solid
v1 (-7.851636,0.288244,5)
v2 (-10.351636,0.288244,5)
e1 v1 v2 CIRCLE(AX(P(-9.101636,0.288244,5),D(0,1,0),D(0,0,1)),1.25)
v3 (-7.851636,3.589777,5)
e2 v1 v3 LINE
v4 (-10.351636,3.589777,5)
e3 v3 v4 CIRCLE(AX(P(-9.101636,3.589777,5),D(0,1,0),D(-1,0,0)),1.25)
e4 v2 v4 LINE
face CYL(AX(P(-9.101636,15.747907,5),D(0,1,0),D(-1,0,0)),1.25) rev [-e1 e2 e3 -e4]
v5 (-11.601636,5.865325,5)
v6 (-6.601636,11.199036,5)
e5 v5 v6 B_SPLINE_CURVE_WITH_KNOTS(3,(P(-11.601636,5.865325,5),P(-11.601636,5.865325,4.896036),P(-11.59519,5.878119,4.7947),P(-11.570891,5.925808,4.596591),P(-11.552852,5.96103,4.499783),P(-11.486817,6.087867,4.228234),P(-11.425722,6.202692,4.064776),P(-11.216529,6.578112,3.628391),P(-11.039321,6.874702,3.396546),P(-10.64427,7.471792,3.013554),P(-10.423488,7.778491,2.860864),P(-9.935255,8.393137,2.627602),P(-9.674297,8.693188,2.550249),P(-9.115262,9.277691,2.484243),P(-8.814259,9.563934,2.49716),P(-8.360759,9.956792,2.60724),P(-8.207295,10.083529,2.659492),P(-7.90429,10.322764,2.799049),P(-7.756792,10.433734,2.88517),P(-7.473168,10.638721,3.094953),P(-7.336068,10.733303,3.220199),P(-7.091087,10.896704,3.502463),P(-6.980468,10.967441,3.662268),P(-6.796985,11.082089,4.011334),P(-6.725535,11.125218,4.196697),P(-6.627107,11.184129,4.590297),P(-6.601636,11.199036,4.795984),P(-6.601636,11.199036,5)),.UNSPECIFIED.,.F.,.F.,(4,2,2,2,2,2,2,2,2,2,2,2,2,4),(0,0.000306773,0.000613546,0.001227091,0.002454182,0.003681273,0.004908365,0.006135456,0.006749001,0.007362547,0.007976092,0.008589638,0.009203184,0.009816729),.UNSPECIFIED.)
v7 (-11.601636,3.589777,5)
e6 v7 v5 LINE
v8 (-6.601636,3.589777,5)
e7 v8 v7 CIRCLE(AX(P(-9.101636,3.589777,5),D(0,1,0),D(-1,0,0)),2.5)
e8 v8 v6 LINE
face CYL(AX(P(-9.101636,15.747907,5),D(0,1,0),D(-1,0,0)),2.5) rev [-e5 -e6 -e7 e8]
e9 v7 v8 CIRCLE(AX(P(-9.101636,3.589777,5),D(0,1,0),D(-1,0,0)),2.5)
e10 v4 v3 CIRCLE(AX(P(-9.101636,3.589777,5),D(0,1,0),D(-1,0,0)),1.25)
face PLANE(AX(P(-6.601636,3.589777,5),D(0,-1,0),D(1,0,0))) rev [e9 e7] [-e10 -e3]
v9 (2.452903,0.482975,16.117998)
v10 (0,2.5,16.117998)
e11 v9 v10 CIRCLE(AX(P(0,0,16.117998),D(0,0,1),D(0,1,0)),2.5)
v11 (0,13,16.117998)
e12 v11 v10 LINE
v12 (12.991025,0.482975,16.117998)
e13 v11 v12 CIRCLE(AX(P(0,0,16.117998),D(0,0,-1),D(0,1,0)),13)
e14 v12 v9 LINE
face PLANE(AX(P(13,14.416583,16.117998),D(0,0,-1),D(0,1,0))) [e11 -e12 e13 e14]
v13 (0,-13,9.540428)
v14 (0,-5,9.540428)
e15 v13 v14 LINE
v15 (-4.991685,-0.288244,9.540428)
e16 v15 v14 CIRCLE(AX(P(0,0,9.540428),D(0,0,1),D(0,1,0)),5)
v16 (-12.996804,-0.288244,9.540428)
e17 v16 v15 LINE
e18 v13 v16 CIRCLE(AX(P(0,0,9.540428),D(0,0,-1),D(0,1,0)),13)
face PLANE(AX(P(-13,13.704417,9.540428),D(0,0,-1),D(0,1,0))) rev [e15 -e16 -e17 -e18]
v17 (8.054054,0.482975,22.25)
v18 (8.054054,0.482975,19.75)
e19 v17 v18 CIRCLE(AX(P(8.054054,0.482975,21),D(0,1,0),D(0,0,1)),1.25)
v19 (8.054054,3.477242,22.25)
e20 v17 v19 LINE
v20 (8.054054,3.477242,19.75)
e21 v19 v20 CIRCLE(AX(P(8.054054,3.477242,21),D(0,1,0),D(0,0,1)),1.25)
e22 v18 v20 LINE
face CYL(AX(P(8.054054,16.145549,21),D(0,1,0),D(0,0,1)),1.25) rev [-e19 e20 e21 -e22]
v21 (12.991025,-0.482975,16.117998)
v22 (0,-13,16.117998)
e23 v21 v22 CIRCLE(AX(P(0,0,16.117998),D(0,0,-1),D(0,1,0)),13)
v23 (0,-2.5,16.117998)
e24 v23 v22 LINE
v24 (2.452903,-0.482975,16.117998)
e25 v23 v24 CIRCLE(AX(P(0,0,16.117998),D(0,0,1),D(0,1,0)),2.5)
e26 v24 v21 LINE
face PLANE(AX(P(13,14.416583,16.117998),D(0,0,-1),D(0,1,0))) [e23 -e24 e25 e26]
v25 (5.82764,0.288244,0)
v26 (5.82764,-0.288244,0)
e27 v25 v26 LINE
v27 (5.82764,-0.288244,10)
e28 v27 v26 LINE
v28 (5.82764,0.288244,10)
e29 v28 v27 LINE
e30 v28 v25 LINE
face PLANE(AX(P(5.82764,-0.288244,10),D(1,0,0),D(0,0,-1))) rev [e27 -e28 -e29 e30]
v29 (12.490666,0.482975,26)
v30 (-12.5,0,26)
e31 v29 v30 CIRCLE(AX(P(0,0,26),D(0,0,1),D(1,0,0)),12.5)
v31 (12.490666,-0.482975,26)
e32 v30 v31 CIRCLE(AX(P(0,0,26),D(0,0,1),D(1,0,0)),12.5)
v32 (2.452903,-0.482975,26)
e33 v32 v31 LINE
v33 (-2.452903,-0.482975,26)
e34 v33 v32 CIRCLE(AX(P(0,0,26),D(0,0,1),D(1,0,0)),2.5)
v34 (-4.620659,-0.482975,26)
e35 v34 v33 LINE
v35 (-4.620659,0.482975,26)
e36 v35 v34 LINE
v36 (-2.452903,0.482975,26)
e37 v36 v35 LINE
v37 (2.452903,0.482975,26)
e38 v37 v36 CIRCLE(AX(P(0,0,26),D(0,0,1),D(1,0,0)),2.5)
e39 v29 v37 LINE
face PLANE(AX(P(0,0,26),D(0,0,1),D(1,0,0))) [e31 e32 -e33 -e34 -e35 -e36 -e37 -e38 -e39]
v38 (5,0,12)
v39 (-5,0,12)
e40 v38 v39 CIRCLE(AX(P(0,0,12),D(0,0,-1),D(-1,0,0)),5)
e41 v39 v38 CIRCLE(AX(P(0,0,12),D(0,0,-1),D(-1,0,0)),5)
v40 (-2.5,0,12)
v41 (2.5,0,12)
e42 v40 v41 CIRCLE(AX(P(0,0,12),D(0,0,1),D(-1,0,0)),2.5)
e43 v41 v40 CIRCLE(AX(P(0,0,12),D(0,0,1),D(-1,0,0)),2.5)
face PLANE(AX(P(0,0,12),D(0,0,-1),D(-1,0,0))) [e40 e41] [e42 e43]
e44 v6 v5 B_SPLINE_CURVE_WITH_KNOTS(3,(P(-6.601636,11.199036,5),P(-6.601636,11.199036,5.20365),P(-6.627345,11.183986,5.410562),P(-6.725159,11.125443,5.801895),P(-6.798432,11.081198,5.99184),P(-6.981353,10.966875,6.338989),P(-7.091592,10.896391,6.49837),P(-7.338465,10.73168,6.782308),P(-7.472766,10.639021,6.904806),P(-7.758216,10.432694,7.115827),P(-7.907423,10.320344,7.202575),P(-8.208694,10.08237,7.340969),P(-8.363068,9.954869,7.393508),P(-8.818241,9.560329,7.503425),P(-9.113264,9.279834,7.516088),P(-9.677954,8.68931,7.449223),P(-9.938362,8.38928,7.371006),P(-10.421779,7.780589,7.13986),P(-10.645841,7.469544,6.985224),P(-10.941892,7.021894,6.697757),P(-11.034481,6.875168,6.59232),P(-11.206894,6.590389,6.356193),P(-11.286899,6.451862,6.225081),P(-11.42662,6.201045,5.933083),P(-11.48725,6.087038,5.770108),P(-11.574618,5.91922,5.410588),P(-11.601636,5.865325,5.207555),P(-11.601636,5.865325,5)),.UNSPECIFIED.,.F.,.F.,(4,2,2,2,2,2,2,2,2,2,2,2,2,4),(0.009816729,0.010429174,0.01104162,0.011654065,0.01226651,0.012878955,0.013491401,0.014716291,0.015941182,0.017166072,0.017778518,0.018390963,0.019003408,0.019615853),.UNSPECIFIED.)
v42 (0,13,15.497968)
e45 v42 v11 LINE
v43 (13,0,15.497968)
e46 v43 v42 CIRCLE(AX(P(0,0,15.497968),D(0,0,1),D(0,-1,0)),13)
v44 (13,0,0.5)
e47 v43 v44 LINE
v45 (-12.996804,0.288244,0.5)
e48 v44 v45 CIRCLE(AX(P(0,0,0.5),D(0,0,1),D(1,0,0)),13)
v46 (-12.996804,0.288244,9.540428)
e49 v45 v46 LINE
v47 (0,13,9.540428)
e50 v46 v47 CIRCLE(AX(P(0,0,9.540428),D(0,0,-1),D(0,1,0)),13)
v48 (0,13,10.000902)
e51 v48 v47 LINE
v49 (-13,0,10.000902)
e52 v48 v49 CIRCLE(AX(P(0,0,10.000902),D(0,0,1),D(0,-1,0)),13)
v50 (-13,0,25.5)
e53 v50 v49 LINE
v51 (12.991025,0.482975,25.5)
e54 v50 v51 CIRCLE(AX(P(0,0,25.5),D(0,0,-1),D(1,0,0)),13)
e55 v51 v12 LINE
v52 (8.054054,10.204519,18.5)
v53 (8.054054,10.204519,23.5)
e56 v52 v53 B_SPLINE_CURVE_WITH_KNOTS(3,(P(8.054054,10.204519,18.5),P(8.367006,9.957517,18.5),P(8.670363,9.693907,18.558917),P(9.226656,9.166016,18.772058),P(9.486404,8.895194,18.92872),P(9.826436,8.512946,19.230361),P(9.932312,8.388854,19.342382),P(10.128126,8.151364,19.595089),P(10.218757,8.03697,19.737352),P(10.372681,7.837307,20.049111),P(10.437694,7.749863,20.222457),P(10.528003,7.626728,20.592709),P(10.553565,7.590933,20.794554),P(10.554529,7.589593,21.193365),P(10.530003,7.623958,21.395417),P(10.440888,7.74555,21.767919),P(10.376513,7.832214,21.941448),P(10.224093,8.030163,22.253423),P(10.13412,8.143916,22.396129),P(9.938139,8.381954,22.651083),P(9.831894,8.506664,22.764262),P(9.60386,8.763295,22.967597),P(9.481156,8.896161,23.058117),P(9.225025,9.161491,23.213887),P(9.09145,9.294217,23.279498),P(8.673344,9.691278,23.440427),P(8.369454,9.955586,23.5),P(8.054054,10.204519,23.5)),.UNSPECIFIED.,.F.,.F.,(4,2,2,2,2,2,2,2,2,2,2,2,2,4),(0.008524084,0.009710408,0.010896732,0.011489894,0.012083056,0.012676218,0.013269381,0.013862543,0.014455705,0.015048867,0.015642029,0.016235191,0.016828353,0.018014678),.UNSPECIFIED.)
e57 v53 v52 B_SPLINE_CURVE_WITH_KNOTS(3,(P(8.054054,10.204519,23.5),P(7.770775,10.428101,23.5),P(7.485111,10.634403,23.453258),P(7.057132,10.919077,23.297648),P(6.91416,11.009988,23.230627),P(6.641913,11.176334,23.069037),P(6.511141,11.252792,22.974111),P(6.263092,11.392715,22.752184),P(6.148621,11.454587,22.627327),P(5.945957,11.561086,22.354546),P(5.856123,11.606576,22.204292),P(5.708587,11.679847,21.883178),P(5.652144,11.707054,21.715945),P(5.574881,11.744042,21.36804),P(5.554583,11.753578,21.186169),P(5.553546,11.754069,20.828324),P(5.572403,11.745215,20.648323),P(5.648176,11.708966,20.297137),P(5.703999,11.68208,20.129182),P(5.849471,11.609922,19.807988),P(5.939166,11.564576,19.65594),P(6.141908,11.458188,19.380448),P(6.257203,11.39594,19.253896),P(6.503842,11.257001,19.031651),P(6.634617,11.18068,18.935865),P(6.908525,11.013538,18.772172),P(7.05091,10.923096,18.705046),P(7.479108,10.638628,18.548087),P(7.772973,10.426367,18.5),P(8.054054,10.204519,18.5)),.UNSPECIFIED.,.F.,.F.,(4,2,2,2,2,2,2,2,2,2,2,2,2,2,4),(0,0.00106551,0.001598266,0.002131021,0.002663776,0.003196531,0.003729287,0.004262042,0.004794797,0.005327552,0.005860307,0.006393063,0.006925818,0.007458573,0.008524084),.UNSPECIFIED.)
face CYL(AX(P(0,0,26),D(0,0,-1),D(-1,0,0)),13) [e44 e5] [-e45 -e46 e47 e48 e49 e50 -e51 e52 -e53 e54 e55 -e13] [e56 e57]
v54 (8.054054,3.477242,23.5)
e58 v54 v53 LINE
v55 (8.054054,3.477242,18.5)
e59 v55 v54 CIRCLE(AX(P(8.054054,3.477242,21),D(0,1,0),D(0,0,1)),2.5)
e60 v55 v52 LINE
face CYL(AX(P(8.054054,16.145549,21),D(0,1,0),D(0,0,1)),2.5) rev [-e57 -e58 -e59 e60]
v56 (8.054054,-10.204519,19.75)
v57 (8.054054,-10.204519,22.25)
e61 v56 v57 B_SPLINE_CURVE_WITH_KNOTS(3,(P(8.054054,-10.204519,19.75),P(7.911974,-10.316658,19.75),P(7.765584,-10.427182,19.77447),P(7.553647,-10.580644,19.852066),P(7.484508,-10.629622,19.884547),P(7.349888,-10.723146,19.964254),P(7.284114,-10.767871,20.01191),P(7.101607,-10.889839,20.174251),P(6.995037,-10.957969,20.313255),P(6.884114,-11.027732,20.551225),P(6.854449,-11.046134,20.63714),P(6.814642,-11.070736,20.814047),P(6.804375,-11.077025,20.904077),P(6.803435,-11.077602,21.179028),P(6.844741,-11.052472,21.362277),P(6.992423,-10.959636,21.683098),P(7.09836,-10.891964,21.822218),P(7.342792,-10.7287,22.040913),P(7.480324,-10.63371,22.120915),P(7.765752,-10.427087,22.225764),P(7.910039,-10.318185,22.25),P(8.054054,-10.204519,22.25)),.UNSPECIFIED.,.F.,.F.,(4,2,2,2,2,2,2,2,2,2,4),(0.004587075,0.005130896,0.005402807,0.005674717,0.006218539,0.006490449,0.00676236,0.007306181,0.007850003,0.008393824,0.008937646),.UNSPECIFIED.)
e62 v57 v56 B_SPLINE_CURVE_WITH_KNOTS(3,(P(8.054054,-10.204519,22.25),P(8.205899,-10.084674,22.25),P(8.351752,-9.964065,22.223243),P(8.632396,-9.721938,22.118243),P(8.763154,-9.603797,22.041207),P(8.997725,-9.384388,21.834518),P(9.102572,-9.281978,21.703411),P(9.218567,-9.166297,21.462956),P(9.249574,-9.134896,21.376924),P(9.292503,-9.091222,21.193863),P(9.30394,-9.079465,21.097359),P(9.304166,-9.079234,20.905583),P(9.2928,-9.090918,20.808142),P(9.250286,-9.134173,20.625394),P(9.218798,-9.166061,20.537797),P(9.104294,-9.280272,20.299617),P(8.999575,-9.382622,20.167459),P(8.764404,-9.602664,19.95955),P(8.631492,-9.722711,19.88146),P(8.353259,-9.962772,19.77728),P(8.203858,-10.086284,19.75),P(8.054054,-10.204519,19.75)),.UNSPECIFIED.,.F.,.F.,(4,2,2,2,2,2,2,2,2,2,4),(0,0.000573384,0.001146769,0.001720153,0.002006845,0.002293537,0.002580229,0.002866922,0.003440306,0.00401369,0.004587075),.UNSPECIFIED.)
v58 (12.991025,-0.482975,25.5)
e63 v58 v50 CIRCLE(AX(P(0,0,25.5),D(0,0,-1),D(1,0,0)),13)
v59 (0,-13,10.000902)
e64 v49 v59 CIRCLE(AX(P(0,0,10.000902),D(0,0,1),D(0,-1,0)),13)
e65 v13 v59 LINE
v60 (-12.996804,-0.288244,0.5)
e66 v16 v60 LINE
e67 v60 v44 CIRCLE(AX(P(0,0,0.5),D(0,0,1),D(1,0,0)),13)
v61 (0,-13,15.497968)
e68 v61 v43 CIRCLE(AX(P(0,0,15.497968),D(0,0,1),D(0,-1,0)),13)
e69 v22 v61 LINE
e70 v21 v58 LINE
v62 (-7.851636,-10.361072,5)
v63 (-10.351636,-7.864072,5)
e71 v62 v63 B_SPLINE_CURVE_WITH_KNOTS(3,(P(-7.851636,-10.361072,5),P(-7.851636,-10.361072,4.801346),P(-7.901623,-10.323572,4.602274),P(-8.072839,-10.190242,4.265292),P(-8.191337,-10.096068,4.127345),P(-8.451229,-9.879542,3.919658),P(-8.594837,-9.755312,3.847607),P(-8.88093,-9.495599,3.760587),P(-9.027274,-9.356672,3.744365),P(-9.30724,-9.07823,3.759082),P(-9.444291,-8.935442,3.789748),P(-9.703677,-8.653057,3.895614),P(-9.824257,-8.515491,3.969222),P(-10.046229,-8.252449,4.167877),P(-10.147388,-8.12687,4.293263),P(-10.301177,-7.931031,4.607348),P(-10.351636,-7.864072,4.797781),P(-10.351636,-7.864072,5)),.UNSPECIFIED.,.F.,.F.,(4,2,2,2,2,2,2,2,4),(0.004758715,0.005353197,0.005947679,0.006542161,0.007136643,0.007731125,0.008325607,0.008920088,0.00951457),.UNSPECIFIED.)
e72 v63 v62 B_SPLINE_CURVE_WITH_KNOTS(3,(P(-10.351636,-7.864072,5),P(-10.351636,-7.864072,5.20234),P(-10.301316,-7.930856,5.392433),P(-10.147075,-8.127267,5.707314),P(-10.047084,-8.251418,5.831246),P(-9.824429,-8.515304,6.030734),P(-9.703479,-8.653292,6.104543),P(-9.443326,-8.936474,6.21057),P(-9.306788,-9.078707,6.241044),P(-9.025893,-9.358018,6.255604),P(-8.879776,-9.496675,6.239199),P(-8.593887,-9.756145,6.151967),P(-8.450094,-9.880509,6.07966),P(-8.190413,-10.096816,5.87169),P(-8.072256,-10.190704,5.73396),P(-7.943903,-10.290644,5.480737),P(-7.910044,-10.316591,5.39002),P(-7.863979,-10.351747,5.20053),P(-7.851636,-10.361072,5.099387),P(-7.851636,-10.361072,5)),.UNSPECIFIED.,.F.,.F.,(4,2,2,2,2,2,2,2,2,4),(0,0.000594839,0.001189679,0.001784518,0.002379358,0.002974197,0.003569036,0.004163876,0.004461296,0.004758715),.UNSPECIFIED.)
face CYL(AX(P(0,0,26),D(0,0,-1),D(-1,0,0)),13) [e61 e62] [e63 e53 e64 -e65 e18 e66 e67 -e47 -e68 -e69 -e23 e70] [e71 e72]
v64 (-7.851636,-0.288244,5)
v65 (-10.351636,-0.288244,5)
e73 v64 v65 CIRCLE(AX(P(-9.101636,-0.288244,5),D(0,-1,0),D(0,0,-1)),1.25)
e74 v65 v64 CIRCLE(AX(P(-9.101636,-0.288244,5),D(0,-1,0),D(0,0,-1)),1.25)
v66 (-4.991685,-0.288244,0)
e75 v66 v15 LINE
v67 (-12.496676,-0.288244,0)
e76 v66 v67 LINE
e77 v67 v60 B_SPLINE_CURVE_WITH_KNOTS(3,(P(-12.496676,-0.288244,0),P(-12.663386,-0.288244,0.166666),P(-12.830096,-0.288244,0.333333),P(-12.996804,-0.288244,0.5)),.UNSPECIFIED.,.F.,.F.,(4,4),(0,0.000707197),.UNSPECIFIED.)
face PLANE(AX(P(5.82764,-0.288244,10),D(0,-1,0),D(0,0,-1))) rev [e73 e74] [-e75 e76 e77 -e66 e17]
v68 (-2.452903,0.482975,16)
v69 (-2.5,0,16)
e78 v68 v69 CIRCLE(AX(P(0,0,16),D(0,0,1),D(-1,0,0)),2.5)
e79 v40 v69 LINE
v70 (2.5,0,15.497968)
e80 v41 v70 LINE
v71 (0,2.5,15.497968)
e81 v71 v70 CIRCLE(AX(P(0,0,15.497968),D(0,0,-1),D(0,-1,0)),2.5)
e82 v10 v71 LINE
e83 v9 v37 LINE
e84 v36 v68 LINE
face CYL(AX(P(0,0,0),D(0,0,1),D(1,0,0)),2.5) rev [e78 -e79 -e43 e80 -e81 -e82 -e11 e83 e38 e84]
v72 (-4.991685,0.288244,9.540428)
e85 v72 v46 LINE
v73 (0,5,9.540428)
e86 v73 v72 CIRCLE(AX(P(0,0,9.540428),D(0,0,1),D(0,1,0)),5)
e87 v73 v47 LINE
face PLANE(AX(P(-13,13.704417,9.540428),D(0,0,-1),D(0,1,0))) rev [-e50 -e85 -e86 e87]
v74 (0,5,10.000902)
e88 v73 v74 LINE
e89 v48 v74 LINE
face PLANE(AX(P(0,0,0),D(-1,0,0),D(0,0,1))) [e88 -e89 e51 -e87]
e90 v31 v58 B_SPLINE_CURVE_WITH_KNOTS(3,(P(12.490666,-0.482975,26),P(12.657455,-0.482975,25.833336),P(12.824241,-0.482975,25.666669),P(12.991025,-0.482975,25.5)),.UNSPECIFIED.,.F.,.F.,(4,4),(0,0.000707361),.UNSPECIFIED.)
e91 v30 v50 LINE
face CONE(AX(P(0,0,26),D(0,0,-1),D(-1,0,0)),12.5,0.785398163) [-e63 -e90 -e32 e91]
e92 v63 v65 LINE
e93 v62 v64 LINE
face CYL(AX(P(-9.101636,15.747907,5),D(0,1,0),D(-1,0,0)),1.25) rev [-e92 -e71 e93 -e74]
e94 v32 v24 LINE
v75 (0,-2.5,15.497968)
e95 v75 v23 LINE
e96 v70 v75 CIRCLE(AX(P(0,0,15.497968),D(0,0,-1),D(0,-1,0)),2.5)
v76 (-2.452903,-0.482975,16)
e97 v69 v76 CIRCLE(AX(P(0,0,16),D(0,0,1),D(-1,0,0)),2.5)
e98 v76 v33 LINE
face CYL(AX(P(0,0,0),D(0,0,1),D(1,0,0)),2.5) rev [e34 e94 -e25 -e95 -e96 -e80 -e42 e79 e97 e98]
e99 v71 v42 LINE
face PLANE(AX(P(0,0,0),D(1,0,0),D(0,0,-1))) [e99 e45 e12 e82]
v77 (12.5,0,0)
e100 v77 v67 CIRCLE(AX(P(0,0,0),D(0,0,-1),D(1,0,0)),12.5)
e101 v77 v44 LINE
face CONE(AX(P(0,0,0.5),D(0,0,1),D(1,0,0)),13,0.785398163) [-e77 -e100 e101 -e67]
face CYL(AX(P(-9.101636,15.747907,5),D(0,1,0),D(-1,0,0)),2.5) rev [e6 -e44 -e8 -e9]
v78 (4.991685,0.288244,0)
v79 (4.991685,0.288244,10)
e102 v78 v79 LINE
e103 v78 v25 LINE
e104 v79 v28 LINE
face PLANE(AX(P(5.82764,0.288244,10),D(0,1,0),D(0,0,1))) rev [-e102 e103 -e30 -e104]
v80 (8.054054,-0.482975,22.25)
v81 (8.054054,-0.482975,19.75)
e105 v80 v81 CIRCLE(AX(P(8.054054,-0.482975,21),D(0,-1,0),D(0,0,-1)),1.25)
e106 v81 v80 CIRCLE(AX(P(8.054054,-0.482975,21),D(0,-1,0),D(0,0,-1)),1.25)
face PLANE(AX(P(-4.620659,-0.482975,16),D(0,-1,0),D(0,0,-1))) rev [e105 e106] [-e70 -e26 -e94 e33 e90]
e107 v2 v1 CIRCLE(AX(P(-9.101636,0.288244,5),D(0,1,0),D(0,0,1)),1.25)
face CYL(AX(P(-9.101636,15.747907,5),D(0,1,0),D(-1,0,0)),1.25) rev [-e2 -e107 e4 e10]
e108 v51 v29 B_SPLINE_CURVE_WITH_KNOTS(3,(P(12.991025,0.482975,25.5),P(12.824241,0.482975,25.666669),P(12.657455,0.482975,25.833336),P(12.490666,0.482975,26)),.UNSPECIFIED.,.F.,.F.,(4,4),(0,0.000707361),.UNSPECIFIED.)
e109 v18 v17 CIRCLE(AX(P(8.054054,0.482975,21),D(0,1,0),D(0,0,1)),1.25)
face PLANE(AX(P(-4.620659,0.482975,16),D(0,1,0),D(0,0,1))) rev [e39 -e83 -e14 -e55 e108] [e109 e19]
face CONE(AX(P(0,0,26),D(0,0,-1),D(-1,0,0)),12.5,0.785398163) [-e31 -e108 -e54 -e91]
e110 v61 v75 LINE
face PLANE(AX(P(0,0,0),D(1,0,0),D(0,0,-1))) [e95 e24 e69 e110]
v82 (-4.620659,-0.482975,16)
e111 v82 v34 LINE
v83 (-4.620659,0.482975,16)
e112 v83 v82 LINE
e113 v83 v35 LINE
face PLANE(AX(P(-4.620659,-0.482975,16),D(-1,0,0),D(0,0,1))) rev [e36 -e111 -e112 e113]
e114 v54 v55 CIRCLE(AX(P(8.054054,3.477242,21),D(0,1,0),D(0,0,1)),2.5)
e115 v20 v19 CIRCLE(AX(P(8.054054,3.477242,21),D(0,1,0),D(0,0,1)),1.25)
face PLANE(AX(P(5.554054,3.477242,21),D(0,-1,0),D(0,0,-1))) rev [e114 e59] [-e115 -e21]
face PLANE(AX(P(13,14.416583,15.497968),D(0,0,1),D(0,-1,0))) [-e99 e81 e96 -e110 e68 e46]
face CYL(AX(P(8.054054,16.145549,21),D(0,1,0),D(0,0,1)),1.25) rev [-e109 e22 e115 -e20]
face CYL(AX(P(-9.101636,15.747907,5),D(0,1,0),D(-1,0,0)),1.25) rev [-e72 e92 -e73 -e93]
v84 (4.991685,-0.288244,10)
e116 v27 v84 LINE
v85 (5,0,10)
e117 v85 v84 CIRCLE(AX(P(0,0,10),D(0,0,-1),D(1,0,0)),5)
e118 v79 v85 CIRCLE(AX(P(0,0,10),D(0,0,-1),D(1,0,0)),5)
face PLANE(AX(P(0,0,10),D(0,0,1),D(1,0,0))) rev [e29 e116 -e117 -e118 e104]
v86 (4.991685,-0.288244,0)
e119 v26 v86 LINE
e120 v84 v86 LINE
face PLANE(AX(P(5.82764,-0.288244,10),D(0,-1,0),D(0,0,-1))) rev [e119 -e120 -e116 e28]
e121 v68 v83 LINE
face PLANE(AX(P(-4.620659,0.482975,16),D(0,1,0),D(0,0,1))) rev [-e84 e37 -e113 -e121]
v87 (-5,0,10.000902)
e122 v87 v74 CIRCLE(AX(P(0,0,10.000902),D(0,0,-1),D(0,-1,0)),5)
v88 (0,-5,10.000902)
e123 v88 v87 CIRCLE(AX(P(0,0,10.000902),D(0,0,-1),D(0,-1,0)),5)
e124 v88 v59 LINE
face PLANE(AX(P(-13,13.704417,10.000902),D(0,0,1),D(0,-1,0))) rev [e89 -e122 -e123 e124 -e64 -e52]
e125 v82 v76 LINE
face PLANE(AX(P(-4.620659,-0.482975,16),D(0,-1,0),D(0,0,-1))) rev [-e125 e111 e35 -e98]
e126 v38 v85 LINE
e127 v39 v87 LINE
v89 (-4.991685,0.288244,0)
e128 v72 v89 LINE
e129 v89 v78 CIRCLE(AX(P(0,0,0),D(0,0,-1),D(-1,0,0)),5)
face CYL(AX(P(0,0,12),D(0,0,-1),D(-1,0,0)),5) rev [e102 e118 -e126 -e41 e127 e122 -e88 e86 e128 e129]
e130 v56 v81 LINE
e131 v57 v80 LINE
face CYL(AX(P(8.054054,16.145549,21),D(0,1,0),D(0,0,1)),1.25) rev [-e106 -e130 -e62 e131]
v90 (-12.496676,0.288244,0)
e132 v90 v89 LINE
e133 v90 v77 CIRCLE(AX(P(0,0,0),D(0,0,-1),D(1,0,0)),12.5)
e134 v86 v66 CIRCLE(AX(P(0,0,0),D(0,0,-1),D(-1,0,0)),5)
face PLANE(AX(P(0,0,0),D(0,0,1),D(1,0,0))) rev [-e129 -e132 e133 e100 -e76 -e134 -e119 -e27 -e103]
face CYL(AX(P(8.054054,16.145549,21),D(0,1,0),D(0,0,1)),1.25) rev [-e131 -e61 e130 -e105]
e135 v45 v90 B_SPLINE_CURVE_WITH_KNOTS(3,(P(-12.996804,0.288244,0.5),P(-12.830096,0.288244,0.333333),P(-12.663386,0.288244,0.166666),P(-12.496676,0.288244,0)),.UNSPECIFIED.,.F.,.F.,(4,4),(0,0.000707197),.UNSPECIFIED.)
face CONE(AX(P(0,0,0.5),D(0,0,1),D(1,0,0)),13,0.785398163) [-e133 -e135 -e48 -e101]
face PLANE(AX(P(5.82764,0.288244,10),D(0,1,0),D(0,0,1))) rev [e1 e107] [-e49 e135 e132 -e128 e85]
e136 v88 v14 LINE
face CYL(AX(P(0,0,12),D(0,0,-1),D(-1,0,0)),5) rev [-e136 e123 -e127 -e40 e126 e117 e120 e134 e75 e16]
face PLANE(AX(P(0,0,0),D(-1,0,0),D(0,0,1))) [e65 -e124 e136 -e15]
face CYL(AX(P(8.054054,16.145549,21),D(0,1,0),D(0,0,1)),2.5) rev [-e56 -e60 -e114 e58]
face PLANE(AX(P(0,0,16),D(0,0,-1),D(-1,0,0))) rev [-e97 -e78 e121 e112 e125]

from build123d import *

# Parameters (mm, degrees)
SKETCH_1_R          = 13
EXTRUDE_1_DEPTH     = 26
SKETCH_2_R          = 2.5
CUT_EXTRUDE_1_DEPTH = 32.843366656
SKETCH_3_R          = 5
CUT_EXTRUDE_2_DEPTH = 12
SKETCH_4_W          = 21.947389444
SKETCH_4_H          = 0.965950114
CUT_EXTRUDE_3_DEPTH = 10
SKETCH_5_W          = 24.42165542
SKETCH_5_H          = 0.576488958
CUT_EXTRUDE_4_DEPTH = 10
SKETCH_6_W          = 0.620030038
SKETCH_6_H          = 28.40124723
CUT_EXTRUDE_5_DEPTH = 32.843366656
SKETCH_7_W          = 0.460474017
SKETCH_7_H          = 28.978503402
CUT_EXTRUDE_6_DEPTH = 32.843366656
CHAMFER_1_SIZE      = 0.5


with BuildPart() as part:
    # 草图1 → 凸台-拉伸1 (new body)
    with BuildSketch(Plane.XY):
        with Locations(Location((0, 0, 0), (0, 0, 180))):
            Circle(SKETCH_1_R)
    extrude(amount=EXTRUDE_1_DEPTH)

    # 草图2 → 切除-拉伸1 (cut, through all)
    with BuildSketch(Plane.XY.offset(26)):
        Circle(SKETCH_2_R)
    extrude(amount=-CUT_EXTRUDE_1_DEPTH, mode=Mode.SUBTRACT)

    # 草图3 → 切除-拉伸2 (cut)
    with BuildSketch(Plane(origin=(0, 0, 0), x_dir=(-1, 0, 0), z_dir=(0, 0, -1))):
        Circle(SKETCH_3_R)
    extrude(amount=-CUT_EXTRUDE_2_DEPTH, mode=Mode.SUBTRACT)

    # 草图4 → 切除-拉伸3 (cut)
    with BuildSketch(Plane.XY.offset(26)):
        with Locations((6.353035437, 0)):
            Rectangle(SKETCH_4_W, SKETCH_4_H)
    extrude(amount=-CUT_EXTRUDE_3_DEPTH, mode=Mode.SUBTRACT)

    # 草图5 → 切除-拉伸4 (cut)
    with BuildSketch(Plane(origin=(0, 0, 0), x_dir=(-1, 0, 0), z_dir=(0, 0, -1))):
        with Locations((6.383187544, 0)):
            Rectangle(SKETCH_5_W, SKETCH_5_H)
    extrude(amount=-CUT_EXTRUDE_4_DEPTH, mode=Mode.SUBTRACT)

    # 草图6 → 切除-拉伸5 (cut, through all)
    with BuildSketch(Plane(origin=(0, 0, 0), x_dir=(0, 0, -1), z_dir=(1, 0, 0))):
        with Locations((-15.807983144, 0.215959177)):
            Rectangle(SKETCH_6_W, SKETCH_6_H)
    extrude(amount=CUT_EXTRUDE_5_DEPTH, mode=Mode.SUBTRACT)

    # 草图7 → 切除-拉伸6 (cut, through all)
    with BuildSketch(Plane(origin=(0, 0, 0), x_dir=(0, 0, -1), z_dir=(1, 0, 0))):
        with Locations((-9.770664876, -0.784834467)):
            Rectangle(SKETCH_7_W, SKETCH_7_H)
    extrude(amount=-CUT_EXTRUDE_6_DEPTH, mode=Mode.SUBTRACT)

    # 草图8 → 切除-旋转1 (revolve, cut)
    with BuildSketch(Plane.XY.offset(21), mode=Mode.PRIVATE) as cut_revolve_1_sk:
        Polygon((5.554054174, 13), (5.554054174, 3.477242408), (6.804054174, 3.477242408), (6.804054174, -12.992472662), (8.054054174, -12.992472662), (8.054054174, 13), align=None)
    revolve(cut_revolve_1_sk.sketch.rotate(Axis((8.054054174, 16.145548825, 21), (0, -1, 0)), 270), axis=Axis((8.054054174, 16.145548825, 21), (0, -1, 0)), mode=Mode.SUBTRACT)

    # 草图9 → 切除-旋转2 (revolve, cut)
    with BuildSketch(Plane(origin=(0, 0, 5), x_dir=(-1, 0, 0), z_dir=(0, 0, -1)), mode=Mode.PRIVATE) as cut_revolve_2_sk:
        Polygon((6.601636039, 12.445267502), (6.601636039, 3.589776819), (7.851636039, 3.589776819), (7.851636039, -11.887089541), (9.101636039, -11.887089541), (9.101636039, 12.445267502), align=None)
    revolve(cut_revolve_2_sk.sketch.rotate(Axis((-9.101636039, 15.747906526, 5), (0, -1, 0)), 180), axis=Axis((-9.101636039, 15.747906526, 5), (0, -1, 0)), mode=Mode.SUBTRACT)

    # 倒角1
    chamfer_1_edges = [part.edges().sort_by_distance(p)[0] for p in [
        (-0.241529218, 12.9977561, 26),
        (13, 0, 0),
    ]]
    chamfer(chamfer_1_edges, length=CHAMFER_1_SIZE)


solid = part.part
